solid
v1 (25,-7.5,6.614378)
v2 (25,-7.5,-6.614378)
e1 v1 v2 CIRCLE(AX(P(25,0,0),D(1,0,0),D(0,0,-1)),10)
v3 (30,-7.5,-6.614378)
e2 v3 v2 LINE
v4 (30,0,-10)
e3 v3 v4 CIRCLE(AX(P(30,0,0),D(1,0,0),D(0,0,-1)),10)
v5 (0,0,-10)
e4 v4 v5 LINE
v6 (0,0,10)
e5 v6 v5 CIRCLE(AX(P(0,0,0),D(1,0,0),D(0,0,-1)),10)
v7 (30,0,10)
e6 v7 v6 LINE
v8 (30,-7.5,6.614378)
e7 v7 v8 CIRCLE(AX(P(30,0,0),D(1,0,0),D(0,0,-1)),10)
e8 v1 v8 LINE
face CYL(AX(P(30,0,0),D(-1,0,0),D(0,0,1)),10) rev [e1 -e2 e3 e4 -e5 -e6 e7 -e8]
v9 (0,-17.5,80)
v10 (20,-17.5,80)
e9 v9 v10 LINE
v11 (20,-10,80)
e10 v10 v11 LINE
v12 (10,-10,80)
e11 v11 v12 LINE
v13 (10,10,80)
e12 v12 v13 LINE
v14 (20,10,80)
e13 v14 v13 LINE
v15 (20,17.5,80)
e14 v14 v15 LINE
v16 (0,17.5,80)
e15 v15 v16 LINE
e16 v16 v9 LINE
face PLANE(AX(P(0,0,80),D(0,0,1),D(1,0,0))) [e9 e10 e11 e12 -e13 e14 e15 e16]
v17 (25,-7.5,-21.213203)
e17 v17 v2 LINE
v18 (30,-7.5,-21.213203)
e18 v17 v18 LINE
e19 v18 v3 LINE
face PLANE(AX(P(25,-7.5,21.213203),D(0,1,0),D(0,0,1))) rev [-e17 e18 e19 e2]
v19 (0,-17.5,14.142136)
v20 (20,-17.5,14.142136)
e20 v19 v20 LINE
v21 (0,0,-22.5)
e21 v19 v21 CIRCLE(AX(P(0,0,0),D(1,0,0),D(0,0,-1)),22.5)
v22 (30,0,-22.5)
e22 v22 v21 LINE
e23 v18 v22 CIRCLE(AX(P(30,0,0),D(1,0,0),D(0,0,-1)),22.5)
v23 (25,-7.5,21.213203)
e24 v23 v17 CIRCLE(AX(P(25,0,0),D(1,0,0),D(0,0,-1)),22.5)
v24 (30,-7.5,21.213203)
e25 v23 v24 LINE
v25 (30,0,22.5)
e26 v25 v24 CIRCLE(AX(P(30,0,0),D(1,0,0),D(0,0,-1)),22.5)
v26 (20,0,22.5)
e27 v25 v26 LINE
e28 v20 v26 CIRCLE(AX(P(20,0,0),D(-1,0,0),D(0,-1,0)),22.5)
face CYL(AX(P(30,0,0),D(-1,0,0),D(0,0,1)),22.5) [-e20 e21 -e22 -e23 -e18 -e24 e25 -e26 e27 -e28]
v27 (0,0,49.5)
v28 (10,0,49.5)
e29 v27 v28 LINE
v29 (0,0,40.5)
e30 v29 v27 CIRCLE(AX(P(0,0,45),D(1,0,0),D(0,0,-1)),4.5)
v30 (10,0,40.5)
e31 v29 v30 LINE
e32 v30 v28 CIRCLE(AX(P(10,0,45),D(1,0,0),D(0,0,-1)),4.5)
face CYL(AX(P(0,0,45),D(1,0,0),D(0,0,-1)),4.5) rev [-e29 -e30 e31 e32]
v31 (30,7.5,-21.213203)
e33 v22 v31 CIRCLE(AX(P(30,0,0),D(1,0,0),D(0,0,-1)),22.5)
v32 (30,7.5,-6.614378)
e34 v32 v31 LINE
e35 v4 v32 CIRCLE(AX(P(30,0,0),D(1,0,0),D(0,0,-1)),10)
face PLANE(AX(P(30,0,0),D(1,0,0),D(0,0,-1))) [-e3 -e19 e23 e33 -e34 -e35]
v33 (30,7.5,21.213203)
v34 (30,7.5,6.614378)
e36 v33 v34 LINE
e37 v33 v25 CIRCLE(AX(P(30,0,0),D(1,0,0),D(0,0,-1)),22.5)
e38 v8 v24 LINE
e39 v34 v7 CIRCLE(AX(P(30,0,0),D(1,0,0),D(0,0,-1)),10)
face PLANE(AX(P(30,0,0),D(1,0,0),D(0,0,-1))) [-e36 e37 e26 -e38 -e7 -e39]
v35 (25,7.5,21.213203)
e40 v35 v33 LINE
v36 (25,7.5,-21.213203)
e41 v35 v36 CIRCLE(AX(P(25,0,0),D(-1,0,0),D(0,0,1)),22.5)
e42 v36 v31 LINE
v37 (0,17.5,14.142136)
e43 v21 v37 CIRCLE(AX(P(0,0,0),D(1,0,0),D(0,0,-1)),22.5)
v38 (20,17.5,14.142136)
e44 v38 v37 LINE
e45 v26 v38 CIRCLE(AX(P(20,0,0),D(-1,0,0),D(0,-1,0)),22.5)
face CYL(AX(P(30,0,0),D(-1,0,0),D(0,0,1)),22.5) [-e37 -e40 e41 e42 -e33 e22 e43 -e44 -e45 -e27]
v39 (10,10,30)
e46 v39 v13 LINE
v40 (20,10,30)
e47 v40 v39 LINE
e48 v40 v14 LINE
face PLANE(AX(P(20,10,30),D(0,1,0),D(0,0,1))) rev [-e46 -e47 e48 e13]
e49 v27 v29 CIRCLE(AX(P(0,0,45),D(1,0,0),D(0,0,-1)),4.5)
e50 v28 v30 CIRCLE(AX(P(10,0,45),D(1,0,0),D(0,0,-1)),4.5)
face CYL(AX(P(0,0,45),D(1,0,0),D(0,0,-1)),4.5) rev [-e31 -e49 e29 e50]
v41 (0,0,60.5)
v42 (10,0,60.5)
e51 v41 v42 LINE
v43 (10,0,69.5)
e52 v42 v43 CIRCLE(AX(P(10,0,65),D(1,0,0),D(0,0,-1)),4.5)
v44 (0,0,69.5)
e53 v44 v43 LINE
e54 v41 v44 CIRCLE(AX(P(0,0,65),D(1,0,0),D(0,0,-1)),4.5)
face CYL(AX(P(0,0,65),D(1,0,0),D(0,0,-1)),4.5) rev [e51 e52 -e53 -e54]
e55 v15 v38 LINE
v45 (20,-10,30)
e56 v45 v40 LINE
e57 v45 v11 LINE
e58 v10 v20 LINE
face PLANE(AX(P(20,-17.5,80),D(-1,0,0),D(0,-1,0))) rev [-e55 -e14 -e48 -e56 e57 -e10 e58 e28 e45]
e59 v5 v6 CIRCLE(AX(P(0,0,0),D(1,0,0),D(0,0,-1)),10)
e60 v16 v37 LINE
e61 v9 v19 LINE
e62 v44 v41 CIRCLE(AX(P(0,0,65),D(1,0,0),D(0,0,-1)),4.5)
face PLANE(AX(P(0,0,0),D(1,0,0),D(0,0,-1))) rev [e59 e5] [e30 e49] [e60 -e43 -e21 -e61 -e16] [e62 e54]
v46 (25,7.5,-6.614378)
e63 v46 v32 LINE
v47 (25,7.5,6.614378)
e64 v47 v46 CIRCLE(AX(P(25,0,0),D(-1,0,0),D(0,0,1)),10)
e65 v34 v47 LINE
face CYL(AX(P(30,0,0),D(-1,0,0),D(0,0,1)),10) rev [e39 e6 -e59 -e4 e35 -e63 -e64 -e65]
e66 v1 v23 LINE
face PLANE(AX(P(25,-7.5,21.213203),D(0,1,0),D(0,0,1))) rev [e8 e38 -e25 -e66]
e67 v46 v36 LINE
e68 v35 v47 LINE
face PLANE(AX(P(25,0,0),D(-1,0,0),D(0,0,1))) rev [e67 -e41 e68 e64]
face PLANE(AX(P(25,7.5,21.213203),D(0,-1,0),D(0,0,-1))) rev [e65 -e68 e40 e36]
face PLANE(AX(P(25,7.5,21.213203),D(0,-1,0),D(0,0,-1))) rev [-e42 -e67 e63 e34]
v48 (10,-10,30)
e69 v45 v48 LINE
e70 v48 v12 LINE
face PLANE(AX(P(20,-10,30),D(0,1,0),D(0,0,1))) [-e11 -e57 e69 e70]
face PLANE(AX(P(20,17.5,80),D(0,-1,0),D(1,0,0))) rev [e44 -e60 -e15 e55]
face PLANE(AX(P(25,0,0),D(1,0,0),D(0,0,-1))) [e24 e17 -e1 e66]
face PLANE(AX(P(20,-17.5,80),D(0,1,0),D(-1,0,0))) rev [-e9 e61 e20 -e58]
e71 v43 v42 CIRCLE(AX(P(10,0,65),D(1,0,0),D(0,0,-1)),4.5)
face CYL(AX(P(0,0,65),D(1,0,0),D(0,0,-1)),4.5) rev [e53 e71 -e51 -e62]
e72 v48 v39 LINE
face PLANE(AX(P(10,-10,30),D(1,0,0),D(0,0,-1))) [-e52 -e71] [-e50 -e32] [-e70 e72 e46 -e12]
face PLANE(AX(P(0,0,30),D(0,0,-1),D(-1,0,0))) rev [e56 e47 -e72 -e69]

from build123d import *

# Parameters (mm, degrees)
HUB_PROFILE_SKETCH_R       = 22.5
HUB_PROFILE_SKETCH_R_2     = 10
HUB_BOSS_45_DEPTH          = 30
HUB_START                  = -5
HUB_FACE_SLOT_15_DEPTH     = 5
HUB_SLOT_STEP_15_DEPTH     = 5
CRANK_ARM_PROFILE_SKETCH_W = 20
CRANK_ARM_PROFILE_SKETCH_H = 35
CRANK_ARM_DEPTH            = 80
BORE_START                 = -80
BORE_SKETCH_R              = 10
BORE_20_DEPTH              = 80
ARM_WINDOW_SKETCH_W        = 10
ARM_WINDOW_SKETCH_H        = 20
ARM_WINDOW_10X20_DEPTH     = 50
ARM_SIDE_CUT_SKETCH_R      = 4.5
ARM_SIDE_CUT_DEPTH         = 86.476604986


with BuildPart() as part:
    # Hub Profile Sketch → Hub Boss Ø45 (new body)
    with BuildSketch(Plane(origin=(0, 0, 0), x_dir=(0, 0, -1), z_dir=(1, 0, 0))):
        Circle(HUB_PROFILE_SKETCH_R)
        Circle(HUB_PROFILE_SKETCH_R_2, mode=Mode.SUBTRACT)
    extrude(amount=HUB_BOSS_45_DEPTH)

    # Hub Face Slot Sketch → Hub Face Slot 15 (cut)
    with BuildSketch(Plane(origin=(30, 0, 0), x_dir=(0, 0, -1), z_dir=(1, 0, 0)).offset(HUB_START)):
        with BuildLine():
            Line((-21.213203436, 7.5), (21.213203436, 7.5))
            ThreePointArc((21.213203436, 7.5), (0, 22.5), (-21.213203436, 7.5))
        make_face()
    extrude(amount=HUB_FACE_SLOT_15_DEPTH, mode=Mode.SUBTRACT)

    # Hub Slot Step Sketch → Hub Slot Step 15 (cut)
    with BuildSketch(Plane(origin=(30, 0, 0), x_dir=(0, 0, -1), z_dir=(1, 0, 0)).offset(HUB_START)):
        with BuildLine():
            Line((-21.213203436, -7.5), (21.213203436, -7.5))
            ThreePointArc((21.213203436, -7.5), (0, -22.5), (-21.213203436, -7.5))
        make_face()
    extrude(amount=HUB_SLOT_STEP_15_DEPTH, mode=Mode.SUBTRACT)

    # Crank Arm Profile Sketch → Crank Arm (add)
    with BuildSketch(Plane.XY):
        with Locations((10, 0)):
            Rectangle(CRANK_ARM_PROFILE_SKETCH_W, CRANK_ARM_PROFILE_SKETCH_H)
    extrude(amount=CRANK_ARM_DEPTH)

    # Bore Sketch → Bore Ø20 (cut)
    with BuildSketch(Plane(origin=(20, 0, 0), x_dir=(0, 0, -1), z_dir=(1, 0, 0)).offset(BORE_START)):
        with Locations(Location((0, 0, 0), (0, 0, 131.409622109))):
            Circle(BORE_SKETCH_R)
    extrude(amount=BORE_20_DEPTH, mode=Mode.SUBTRACT)

    # Arm Window Sketch → Arm Window 10x20 (cut)
    with BuildSketch(Plane.XY.offset(80)):
        with Locations((15, 0)):
            Rectangle(ARM_WINDOW_SKETCH_W, ARM_WINDOW_SKETCH_H)
    extrude(amount=-ARM_WINDOW_10X20_DEPTH, mode=Mode.SUBTRACT)

    # Arm Side Cut Sketch → Arm Side Cut (cut, through all)
    with BuildSketch(Plane(origin=(10, 0, 0), x_dir=(0, 0, -1), z_dir=(1, 0, 0))):
        with Locations((-65, 0)):
            Circle(ARM_SIDE_CUT_SKETCH_R)
        with Locations((-45, 0)):
            Circle(ARM_SIDE_CUT_SKETCH_R)
    extrude(amount=-ARM_SIDE_CUT_DEPTH, mode=Mode.SUBTRACT)


solid = part.part
